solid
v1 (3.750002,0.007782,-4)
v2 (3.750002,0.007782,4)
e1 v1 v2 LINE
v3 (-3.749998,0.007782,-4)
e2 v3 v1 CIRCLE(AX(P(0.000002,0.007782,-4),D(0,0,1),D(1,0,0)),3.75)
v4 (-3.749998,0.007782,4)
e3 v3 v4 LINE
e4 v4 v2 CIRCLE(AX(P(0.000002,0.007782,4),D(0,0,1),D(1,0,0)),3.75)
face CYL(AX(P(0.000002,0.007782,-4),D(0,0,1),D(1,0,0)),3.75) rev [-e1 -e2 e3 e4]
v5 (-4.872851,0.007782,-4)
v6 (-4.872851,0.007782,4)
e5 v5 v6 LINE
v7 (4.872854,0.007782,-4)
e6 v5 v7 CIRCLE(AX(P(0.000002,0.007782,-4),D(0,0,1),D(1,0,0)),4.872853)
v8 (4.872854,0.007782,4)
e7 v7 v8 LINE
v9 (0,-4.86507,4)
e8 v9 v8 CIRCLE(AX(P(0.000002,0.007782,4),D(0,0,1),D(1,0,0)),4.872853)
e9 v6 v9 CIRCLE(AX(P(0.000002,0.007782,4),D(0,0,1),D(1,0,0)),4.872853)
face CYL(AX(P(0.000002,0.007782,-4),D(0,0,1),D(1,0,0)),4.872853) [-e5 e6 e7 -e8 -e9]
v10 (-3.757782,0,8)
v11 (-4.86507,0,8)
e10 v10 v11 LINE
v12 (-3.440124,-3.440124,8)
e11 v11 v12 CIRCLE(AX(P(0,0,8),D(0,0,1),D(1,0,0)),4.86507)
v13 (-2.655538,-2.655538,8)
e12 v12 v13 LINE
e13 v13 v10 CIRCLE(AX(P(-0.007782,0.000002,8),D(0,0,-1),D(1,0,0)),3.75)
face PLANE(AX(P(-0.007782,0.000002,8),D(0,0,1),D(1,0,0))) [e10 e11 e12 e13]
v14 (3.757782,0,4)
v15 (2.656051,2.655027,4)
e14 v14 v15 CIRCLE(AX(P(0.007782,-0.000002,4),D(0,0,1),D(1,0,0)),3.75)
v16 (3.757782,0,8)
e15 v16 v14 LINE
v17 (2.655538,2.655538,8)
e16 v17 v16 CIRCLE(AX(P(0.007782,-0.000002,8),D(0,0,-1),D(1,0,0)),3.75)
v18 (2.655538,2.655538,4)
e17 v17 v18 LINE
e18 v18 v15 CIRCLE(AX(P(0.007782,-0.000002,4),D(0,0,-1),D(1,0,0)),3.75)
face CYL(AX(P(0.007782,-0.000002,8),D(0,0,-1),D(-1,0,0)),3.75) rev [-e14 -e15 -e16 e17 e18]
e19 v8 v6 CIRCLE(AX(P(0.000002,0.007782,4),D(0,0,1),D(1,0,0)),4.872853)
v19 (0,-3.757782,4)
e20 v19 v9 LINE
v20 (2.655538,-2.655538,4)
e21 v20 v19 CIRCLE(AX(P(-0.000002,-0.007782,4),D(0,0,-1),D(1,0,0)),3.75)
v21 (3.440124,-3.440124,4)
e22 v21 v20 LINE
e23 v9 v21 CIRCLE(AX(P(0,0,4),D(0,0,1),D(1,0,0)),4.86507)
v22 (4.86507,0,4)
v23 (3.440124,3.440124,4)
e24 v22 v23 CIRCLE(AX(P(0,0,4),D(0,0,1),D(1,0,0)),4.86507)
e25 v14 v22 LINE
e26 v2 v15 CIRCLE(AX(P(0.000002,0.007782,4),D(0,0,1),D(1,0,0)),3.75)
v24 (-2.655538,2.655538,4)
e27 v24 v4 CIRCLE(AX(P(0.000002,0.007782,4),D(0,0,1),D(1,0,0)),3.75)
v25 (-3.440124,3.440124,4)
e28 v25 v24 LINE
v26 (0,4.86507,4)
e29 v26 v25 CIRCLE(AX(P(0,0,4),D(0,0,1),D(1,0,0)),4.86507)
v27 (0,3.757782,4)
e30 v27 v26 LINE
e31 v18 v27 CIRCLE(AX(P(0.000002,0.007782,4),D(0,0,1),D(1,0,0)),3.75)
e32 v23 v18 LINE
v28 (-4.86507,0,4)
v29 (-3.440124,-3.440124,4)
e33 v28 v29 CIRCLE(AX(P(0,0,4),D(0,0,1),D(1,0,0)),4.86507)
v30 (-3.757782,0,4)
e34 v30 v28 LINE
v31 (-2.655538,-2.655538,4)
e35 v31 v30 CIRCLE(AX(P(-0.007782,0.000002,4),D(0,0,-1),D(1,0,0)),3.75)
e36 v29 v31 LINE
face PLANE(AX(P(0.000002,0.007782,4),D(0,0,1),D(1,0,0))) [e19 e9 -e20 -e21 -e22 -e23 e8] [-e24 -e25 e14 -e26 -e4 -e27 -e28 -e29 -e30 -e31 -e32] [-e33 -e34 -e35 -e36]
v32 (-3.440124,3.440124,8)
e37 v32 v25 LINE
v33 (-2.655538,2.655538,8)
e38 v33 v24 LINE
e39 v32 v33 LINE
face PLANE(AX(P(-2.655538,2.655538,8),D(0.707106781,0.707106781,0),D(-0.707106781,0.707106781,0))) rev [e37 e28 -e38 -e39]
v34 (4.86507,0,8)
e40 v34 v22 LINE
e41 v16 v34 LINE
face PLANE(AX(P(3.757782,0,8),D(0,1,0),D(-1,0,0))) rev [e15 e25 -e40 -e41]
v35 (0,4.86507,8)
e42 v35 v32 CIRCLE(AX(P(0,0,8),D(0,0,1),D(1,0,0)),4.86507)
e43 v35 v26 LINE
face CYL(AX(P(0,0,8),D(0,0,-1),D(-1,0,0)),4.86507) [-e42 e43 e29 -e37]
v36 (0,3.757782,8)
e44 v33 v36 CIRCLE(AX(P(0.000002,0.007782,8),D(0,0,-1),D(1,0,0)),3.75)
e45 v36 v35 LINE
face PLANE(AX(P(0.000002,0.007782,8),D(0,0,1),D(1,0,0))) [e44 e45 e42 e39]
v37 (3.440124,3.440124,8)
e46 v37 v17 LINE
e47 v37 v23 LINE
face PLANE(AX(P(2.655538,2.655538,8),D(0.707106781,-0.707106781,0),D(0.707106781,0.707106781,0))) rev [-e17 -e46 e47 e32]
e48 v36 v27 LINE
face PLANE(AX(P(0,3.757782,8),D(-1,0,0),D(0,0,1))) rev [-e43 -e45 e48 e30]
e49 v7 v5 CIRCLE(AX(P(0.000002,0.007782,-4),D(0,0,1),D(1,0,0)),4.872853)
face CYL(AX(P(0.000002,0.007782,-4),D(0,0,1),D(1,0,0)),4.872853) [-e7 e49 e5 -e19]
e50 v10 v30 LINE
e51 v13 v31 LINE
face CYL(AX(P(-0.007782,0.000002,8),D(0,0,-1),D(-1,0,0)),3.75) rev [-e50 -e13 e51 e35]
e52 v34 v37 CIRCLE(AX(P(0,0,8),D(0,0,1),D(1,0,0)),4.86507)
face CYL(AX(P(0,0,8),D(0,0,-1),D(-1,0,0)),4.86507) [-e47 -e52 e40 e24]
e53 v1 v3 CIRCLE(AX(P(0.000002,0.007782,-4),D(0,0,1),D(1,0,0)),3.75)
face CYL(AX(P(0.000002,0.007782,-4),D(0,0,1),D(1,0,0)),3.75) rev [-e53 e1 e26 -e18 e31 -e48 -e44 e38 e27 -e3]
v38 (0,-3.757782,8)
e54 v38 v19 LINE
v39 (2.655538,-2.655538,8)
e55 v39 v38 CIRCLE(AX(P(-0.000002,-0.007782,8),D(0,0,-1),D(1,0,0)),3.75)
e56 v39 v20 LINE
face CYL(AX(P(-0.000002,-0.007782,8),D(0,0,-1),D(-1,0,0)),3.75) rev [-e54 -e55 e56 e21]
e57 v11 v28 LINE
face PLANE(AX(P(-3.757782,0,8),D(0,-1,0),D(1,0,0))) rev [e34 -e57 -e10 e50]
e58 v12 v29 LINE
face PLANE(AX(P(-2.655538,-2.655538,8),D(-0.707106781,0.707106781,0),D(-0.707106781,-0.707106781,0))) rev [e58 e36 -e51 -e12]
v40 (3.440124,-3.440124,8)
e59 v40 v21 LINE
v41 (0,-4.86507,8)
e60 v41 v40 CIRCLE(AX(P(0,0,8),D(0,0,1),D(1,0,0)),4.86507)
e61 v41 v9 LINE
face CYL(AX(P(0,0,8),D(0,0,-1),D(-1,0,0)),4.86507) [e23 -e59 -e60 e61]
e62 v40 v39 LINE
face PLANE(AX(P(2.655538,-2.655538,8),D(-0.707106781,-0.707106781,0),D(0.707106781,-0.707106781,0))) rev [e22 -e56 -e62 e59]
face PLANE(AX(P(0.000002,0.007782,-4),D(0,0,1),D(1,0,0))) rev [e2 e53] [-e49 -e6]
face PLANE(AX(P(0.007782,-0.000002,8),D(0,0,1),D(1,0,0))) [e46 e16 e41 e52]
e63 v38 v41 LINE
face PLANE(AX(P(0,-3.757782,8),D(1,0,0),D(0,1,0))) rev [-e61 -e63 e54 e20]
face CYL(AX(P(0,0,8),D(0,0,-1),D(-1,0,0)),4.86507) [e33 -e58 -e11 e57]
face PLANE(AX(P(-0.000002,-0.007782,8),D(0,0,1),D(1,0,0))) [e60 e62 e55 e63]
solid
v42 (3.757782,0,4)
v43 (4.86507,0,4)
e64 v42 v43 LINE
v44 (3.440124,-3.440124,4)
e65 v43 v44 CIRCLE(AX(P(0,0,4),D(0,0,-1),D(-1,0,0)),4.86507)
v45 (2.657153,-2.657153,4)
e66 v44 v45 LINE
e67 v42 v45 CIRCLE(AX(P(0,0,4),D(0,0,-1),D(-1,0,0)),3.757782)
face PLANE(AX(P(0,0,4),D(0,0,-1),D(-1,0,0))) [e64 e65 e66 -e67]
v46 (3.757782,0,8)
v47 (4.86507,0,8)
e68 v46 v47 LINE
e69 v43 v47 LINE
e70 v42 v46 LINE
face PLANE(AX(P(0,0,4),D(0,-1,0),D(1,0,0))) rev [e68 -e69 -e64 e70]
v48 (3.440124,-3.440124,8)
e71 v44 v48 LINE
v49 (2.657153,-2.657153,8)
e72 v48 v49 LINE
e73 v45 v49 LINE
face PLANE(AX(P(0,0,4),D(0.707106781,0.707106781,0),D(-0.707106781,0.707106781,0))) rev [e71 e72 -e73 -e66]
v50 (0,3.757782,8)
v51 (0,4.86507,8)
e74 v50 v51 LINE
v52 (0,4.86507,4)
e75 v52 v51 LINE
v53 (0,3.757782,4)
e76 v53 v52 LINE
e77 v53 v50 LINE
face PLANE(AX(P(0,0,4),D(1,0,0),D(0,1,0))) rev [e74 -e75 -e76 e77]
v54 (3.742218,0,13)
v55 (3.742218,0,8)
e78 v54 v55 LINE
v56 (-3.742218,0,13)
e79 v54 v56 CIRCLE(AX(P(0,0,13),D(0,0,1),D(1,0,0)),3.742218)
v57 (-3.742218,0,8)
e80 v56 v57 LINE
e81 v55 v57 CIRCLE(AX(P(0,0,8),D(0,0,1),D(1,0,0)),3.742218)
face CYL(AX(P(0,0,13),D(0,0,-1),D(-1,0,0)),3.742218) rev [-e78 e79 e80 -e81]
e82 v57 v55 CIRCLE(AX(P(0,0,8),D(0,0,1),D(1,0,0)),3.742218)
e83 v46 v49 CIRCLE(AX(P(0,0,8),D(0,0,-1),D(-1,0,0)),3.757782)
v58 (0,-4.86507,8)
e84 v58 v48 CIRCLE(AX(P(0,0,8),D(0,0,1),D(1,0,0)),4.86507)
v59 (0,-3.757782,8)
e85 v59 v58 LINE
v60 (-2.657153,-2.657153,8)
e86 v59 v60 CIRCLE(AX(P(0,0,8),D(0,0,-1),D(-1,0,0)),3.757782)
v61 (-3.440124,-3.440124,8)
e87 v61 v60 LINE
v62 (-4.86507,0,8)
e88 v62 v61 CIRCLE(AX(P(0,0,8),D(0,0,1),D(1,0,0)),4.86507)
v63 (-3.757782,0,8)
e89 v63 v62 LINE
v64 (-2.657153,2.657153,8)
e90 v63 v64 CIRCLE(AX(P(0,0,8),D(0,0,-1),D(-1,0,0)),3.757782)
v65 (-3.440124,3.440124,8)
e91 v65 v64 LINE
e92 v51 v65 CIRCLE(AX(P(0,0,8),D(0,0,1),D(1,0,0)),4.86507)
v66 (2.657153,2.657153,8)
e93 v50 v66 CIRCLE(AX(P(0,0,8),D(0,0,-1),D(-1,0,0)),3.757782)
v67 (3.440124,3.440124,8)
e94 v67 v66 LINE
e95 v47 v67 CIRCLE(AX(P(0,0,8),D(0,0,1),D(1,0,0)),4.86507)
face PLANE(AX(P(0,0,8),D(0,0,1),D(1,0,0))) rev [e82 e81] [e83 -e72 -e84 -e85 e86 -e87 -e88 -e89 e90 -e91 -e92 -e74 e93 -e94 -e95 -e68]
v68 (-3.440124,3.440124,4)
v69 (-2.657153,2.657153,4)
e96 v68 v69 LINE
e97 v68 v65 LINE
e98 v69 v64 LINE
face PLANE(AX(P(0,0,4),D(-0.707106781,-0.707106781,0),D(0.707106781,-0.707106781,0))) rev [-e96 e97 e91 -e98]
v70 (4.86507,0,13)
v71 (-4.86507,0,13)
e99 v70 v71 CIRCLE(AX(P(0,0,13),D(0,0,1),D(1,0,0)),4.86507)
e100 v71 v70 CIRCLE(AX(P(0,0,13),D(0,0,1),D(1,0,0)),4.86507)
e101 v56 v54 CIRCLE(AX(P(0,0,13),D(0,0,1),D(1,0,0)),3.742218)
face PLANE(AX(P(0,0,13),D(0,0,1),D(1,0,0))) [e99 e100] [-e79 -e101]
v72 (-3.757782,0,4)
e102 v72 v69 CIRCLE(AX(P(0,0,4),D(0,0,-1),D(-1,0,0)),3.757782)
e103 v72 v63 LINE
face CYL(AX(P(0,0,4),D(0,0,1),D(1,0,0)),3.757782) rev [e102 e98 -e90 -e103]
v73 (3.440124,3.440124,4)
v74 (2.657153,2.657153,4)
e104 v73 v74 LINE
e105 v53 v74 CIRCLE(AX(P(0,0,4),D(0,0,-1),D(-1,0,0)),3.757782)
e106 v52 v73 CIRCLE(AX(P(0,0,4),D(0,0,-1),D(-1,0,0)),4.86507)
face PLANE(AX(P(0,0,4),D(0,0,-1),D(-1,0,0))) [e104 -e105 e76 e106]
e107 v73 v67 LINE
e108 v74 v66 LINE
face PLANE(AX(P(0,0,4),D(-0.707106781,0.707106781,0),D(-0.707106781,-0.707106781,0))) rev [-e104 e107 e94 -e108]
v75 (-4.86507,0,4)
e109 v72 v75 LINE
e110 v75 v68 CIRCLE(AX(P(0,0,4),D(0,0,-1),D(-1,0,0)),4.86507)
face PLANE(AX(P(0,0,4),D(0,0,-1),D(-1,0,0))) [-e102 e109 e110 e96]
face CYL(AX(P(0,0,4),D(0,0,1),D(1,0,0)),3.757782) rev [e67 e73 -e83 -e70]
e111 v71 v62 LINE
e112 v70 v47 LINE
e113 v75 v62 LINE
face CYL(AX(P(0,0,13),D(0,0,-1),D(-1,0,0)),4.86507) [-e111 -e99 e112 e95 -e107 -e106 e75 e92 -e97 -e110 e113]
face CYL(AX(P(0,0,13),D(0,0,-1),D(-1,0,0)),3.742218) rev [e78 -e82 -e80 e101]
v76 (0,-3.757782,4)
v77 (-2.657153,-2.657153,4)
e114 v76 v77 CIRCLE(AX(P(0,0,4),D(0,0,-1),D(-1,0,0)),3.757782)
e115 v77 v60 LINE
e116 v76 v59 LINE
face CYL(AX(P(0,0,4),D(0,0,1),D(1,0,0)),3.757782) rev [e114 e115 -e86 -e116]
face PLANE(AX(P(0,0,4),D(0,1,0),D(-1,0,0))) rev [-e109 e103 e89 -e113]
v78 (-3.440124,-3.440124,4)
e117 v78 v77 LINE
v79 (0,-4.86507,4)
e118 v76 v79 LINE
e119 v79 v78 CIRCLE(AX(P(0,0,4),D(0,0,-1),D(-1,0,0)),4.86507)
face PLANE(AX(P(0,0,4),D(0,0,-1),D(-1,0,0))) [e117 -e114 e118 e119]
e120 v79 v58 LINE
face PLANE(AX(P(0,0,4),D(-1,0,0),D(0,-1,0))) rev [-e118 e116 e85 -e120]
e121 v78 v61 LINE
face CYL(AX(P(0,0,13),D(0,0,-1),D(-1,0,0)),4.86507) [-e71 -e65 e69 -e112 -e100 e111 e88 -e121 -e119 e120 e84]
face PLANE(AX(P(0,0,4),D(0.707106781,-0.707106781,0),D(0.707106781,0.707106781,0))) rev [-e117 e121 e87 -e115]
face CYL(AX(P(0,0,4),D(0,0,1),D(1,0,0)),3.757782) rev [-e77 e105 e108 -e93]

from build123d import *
from build123d.topology import SkipClean

# Parameters (mm, degrees)
BOSS_EXTRUDE1_DEPTH      = 4
BOSS_EXTRUDE1_DEPTH_BACK = 4
SKETCH1_R                = 4.872852562
SKETCH1_R_2              = 3.75
BOSS_EXTRUDE2_DEPTH      = 4
SKETCH4_R                = 4.865070387
SKETCH4_R_2              = 3.742217825
BOSS_EXTRUDE3_DEPTH      = 5
BOSS_EXTRUDE4_START      = 4
BOSS_EXTRUDE4_DEPTH      = 4


with BuildPart() as part:
    # Sketch1 → Boss-Extrude1 (new, two sides: drawn at the far end of the back side and taken through both)
    with BuildSketch(Plane.XY.offset(-BOSS_EXTRUDE1_DEPTH_BACK)):
        with Locations((1.501e-06, 0.007782175)):
            Circle(SKETCH1_R)
        with Locations((1.501e-06, 0.007782175)):
            Circle(SKETCH1_R_2, mode=Mode.SUBTRACT)
    extrude(amount=BOSS_EXTRUDE1_DEPTH + BOSS_EXTRUDE1_DEPTH_BACK)

    # Sketch3 → Boss-Extrude2 (add)
    with BuildSketch(Plane.XY.offset(4)):
        with BuildLine():
            Line((0, 3.757782175), (0, 4.865070387))
            ThreePointArc((0, 4.865070387), (-1.861781834, 4.494738955), (-3.440124262, 3.440124262))
            Line((-3.440124262, 3.440124262), (-2.65553791, 2.65553791))
            ThreePointArc((-2.65553791, 2.65553791), (-1.437604143, 3.471276077), (0, 3.757782175))
        make_face()
        with BuildLine():
            Line((3.757782175, 0), (4.865070387, 0))
            ThreePointArc((4.865070387, 0), (4.494738955, 1.861781834), (3.440124262, 3.440124262))
            Line((3.440124262, 3.440124262), (2.65553791, 2.65553791))
            ThreePointArc((2.65553791, 2.65553791), (3.471276077, 1.437604143), (3.757782175, 0))
        make_face()
        with BuildLine():
            Line((0, -3.757782175), (0, -4.865070387))
            ThreePointArc((0, -4.865070387), (1.861781834, -4.494738955), (3.440124262, -3.440124262))
            Line((3.440124262, -3.440124262), (2.65553791, -2.65553791))
            ThreePointArc((2.65553791, -2.65553791), (1.437604143, -3.471276077), (0, -3.757782175))
        make_face()
        with BuildLine():
            Line((-3.757782175, 0), (-4.865070387, 0))
            ThreePointArc((-4.865070387, 0), (-4.494738955, -1.861781834), (-3.440124262, -3.440124262))
            Line((-3.440124262, -3.440124262), (-2.65553791, -2.65553791))
            ThreePointArc((-2.65553791, -2.65553791), (-3.471276077, -1.437604143), (-3.757782175, 0))
        make_face()
    extrude(amount=BOSS_EXTRUDE2_DEPTH)


with BuildPart() as body_2:
    # Sketch4 → Boss-Extrude3 (new body)
    with BuildSketch(Plane.XY.offset(8)):
        Circle(SKETCH4_R)
        Circle(SKETCH4_R_2, mode=Mode.SUBTRACT)
    extrude(amount=BOSS_EXTRUDE3_DEPTH)

    # Sketch5 → Boss-Extrude4 (add)
    with SkipClean():  # the faces are left unmerged after this step: merging them gives an invalid solid
        with BuildSketch(Plane(origin=(0, 0, 8), x_dir=(-1, 0, 0), z_dir=(0, 0, -1)).offset(BOSS_EXTRUDE4_START)):
            with BuildLine():
                Line((0, 3.757782175), (0, 4.865070387))
                ThreePointArc((0, 4.865070387), (-1.861781834, 4.494738955), (-3.440124261, 3.440124261))
                Line((-3.440124262, 3.440124262), (-2.657153258, 2.657153258))
                ThreePointArc((-2.657153258, 2.657153258), (-1.438040981, 3.471738039), (0, 3.757782175))
            make_face()
            with BuildLine():
                ThreePointArc((2.657153258, 2.657153258), (3.471738039, 1.438040981), (3.757782175, 0))
                Line((3.757782175, 0), (4.865070387, 0))
                ThreePointArc((4.865070387, 0), (4.494738955, 1.861781834), (3.440124262, 3.440124262))
                Line((3.440124262, 3.440124262), (2.657153258, 2.657153258))
            make_face()
            with BuildLine():
                ThreePointArc((-4.865070387, 0), (-4.494738955, -1.861781834), (-3.440124261, -3.440124261))
                Line((-3.440124262, -3.440124262), (-2.657153258, -2.657153258))
                ThreePointArc((-2.657153258, -2.657153258), (-3.471738039, -1.438040981), (-3.757782175, 0))
                Line((-3.757782175, 0), (-4.865070387, 0))
            make_face()
            with BuildLine():
                ThreePointArc((0, -4.865070387), (1.861781834, -4.494738955), (3.440124262, -3.440124262))
                Line((3.440124262, -3.440124262), (2.657153258, -2.657153258))
                ThreePointArc((2.657153258, -2.657153258), (1.438040981, -3.471738039), (0, -3.757782175))
                Line((0, -3.757782175), (0, -4.865070387))
            make_face()
        extrude(amount=-BOSS_EXTRUDE4_DEPTH)


solid = Compound([part.part, body_2.part])
